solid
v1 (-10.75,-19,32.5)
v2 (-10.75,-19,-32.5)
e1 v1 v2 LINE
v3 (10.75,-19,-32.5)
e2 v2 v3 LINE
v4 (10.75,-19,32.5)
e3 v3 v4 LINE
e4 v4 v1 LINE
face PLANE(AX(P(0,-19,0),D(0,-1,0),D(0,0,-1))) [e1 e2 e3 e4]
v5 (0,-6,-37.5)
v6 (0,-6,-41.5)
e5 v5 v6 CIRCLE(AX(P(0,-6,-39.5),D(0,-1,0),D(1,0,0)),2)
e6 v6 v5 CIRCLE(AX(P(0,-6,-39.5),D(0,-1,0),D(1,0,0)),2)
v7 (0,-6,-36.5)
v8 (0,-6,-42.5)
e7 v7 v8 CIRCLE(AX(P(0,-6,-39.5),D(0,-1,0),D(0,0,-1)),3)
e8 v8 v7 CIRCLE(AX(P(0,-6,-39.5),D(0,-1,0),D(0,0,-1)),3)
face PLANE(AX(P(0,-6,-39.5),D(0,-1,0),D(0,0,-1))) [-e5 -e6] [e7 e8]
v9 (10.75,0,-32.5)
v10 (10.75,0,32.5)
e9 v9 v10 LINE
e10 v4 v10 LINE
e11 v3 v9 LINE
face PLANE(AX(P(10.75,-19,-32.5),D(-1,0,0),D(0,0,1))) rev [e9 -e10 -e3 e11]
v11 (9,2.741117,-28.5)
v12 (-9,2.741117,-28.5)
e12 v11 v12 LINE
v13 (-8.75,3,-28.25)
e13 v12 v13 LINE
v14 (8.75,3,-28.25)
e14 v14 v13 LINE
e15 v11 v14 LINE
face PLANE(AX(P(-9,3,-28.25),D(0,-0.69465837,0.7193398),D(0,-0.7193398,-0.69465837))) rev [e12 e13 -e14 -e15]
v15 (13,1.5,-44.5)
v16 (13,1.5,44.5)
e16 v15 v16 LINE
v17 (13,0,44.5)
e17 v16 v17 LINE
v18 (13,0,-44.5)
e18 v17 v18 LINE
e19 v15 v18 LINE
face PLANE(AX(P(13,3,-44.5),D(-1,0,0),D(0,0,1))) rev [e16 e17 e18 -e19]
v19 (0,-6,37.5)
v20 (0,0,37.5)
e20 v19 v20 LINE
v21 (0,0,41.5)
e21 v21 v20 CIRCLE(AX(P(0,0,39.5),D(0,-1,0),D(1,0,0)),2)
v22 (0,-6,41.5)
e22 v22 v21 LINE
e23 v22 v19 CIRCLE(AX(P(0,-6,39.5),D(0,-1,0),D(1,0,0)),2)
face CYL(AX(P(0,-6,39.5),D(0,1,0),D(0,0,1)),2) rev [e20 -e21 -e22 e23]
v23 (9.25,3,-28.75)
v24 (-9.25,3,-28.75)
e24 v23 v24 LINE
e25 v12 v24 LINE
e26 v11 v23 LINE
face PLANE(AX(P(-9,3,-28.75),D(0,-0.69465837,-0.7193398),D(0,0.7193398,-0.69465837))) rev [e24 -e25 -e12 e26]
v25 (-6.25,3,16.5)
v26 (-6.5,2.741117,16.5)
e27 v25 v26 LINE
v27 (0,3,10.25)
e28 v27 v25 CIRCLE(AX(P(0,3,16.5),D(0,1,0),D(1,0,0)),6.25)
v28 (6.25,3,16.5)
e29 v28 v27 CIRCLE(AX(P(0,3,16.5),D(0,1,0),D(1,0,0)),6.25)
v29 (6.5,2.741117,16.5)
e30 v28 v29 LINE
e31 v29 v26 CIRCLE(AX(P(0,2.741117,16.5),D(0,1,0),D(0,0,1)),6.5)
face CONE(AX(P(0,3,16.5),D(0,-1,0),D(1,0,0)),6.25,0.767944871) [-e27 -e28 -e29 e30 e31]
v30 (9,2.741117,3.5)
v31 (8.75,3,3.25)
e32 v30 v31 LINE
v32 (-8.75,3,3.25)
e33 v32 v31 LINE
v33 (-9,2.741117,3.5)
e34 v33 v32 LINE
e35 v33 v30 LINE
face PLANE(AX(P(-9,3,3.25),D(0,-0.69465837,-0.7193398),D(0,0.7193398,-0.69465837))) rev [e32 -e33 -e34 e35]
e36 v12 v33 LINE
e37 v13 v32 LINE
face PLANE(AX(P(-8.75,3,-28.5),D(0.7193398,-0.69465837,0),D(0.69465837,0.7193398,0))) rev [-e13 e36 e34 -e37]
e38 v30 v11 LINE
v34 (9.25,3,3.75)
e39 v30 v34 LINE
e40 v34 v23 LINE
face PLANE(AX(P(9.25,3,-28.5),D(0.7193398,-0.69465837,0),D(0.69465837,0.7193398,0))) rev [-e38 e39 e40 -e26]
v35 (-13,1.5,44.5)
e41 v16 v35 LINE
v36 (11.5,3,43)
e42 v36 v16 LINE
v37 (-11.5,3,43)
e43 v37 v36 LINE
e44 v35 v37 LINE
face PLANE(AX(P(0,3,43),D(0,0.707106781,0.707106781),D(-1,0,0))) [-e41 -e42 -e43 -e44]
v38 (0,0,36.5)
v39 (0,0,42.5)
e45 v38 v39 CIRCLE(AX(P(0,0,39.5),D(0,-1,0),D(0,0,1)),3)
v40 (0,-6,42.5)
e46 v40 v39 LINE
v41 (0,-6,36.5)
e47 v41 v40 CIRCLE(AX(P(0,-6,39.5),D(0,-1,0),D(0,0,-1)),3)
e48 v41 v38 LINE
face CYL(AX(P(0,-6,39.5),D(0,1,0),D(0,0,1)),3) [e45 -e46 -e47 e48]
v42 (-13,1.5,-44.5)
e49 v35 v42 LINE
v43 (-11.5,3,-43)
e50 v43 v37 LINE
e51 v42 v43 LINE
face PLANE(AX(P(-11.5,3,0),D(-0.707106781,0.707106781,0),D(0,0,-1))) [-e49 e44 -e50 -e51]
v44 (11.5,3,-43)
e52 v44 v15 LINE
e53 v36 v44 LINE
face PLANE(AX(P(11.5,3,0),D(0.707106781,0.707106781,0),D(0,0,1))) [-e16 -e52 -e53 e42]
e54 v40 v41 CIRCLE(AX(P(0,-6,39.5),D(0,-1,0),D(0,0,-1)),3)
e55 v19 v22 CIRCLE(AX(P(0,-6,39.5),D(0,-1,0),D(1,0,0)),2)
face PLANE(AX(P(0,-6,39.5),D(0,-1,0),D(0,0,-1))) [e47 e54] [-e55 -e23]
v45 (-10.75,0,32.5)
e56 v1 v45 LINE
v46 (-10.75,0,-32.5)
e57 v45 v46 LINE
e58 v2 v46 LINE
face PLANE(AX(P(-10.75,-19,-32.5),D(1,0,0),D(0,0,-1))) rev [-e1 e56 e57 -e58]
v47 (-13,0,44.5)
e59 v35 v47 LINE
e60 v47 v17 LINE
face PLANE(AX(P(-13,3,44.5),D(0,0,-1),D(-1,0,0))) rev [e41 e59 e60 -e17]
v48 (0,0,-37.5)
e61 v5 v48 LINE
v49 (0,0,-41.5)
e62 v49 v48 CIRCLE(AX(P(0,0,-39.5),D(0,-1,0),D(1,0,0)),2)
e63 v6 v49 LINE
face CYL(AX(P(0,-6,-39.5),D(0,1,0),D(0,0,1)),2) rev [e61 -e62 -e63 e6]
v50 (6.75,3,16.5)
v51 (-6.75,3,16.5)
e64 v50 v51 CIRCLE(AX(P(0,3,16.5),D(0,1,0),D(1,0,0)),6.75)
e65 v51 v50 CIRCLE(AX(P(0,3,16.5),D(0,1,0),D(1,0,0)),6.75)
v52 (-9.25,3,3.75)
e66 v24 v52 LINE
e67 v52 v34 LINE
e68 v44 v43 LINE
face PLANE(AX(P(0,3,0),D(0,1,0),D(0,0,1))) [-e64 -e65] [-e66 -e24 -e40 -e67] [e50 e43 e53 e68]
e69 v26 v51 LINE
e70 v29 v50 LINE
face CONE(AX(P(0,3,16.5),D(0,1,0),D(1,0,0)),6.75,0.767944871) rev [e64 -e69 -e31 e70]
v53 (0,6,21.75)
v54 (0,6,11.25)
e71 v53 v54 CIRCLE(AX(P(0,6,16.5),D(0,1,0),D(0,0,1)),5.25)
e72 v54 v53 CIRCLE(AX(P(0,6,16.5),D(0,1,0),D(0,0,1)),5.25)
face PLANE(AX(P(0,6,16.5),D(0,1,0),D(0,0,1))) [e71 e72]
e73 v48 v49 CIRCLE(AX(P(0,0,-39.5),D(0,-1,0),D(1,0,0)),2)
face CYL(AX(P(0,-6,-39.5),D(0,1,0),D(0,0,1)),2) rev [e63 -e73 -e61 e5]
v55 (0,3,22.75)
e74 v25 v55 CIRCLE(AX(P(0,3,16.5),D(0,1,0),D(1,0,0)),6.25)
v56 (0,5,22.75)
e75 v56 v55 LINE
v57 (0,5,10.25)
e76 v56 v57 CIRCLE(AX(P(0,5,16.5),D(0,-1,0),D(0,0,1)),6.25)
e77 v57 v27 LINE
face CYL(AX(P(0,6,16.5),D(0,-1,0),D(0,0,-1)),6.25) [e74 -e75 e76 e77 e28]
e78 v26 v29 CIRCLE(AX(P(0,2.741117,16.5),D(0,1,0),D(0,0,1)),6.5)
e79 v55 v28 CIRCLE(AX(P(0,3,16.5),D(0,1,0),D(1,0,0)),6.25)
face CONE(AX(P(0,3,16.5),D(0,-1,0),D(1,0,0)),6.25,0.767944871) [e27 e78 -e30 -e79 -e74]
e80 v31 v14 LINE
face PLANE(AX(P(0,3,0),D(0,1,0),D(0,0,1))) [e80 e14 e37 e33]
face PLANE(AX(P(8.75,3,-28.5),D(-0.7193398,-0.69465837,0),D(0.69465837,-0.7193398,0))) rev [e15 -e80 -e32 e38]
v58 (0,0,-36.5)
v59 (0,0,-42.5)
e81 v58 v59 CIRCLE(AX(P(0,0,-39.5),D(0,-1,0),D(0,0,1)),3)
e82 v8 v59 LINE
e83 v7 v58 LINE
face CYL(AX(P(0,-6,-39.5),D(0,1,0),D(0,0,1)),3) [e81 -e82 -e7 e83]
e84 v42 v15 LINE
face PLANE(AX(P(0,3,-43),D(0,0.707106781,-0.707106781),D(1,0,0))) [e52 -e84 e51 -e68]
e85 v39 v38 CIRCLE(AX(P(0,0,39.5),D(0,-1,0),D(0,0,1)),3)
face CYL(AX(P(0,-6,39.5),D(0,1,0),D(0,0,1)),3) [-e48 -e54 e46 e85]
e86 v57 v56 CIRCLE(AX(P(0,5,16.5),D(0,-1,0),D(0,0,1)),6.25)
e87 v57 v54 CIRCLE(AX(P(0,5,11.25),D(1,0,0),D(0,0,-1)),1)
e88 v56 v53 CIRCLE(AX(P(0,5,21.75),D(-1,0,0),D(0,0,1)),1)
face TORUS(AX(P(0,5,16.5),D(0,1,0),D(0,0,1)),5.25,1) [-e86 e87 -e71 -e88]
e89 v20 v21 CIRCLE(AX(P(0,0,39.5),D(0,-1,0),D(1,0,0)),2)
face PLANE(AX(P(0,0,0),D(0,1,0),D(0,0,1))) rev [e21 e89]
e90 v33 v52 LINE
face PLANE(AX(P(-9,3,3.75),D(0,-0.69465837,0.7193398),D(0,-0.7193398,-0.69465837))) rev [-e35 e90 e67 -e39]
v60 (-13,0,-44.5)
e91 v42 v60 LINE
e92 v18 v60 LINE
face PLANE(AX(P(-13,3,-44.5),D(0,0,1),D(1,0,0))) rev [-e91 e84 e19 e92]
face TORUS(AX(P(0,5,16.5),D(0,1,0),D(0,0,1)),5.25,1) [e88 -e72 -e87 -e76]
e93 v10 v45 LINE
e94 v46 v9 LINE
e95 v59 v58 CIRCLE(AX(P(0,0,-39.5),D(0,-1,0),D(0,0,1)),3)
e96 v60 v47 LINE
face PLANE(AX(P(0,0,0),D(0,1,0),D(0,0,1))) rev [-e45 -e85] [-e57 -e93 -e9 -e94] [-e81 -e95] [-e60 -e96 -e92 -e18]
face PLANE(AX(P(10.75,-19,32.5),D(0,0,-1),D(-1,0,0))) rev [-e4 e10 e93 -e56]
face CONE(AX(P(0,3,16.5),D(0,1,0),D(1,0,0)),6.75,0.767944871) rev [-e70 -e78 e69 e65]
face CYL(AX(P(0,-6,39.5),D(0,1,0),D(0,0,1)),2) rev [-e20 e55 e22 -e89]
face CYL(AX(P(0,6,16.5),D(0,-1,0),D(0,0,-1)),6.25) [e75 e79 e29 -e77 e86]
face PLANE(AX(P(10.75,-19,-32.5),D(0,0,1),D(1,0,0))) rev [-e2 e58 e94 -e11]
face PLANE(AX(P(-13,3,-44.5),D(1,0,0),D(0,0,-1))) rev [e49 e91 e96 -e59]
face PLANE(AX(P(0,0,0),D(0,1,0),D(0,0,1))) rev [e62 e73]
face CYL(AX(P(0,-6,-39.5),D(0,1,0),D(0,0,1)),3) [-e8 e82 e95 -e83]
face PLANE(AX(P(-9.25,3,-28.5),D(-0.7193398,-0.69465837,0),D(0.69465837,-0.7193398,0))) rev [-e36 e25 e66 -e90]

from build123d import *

# Parameters (mm, degrees)
SKETCH1_W               = 26
SKETCH1_H               = 89
BOSS_EXTRUDE1_DEPTH     = 3
SKETCH2_R               = 6.75
SKETCH2_R_2             = 6.25
SKETCH2_W               = 18.5
SKETCH2_H               = 32.5
SKETCH2_W_2             = 17.5
SKETCH2_H_2             = 31.5
CUT_EXTRUDE_THIN1_DEPTH = 1
CUT_EXTRUDE_THIN1_TAPER = 44
SKETCH3_R               = 6.25
BOSS_EXTRUDE2_DEPTH     = 3
FILLET1_R               = 1
CHAMFER1_SIZE           = 1.5
SKETCH4_R               = 3
SKETCH4_R_2             = 2
EXTRUDE_THIN2_DEPTH     = 6
SKETCH5_W               = 21.5
SKETCH5_H               = 65
BOSS_EXTRUDE3_DEPTH     = 19


with BuildPart() as part:
    # Sketch1 → Boss-Extrude1 (new body)
    with BuildSketch(Plane(origin=(0, 0, 0), x_dir=(1, 0, 0), z_dir=(0, 1, 0))):
        Rectangle(SKETCH1_W, SKETCH1_H)
    extrude(amount=BOSS_EXTRUDE1_DEPTH)

    # Sketch2 → Cut-Extrude-Thin1 (cut)
    # profile 1 of 2: a face of its own
    with BuildSketch(Plane(origin=(0, 3, 0), x_dir=(1, 0, 0), z_dir=(0, 1, 0))):
        with Locations((0, -16.5)):
            Circle(SKETCH2_R)
        with Locations((0, -16.5)):
            Circle(SKETCH2_R_2, mode=Mode.SUBTRACT)
    # profile 2 of 2: a face of its own
    with BuildSketch(Plane(origin=(0, 3, 0), x_dir=(1, 0, 0), z_dir=(0, 1, 0))):
        with Locations((0, 12.5)):
            Rectangle(SKETCH2_W, SKETCH2_H)
        with Locations((0, 12.5)):
            Rectangle(SKETCH2_W_2, SKETCH2_H_2, mode=Mode.SUBTRACT)
    extrude(amount=-CUT_EXTRUDE_THIN1_DEPTH, taper=CUT_EXTRUDE_THIN1_TAPER, mode=Mode.SUBTRACT)

    # Sketch3 → Boss-Extrude2 (add)
    with BuildSketch(Plane(origin=(0, 3, 0), x_dir=(1, 0, 0), z_dir=(0, 1, 0))):
        with Locations((0, -16.5)):
            Circle(SKETCH3_R)
    extrude(amount=BOSS_EXTRUDE2_DEPTH)

    # Fillet1
    fillet1_edges = [part.edges().sort_by_distance(p)[0] for p in [
        (-6.25, 6, 16.5),
    ]]
    fillet(fillet1_edges, radius=FILLET1_R)

    # Chamfer1
    chamfer1_edges = [part.edges().sort_by_distance(p)[0] for p in [
        (-13, 3, 0),
        (0, 3, 44.5),
        (13, 3, 0),
        (0, 3, -44.5),
    ]]
    chamfer(chamfer1_edges, length=CHAMFER1_SIZE)

    # Sketch4 → Extrude-Thin2 (add)
    # profile 1 of 2: a face of its own
    with BuildSketch(Plane.XZ):
        with Locations((0, -39.5)):
            Circle(SKETCH4_R)
        with Locations((0, -39.5)):
            Circle(SKETCH4_R_2, mode=Mode.SUBTRACT)
    # profile 2 of 2: a face of its own
    with BuildSketch(Plane.XZ):
        with Locations((0, 39.5)):
            Circle(SKETCH4_R)
        with Locations((0, 39.5)):
            Circle(SKETCH4_R_2, mode=Mode.SUBTRACT)
    extrude(amount=EXTRUDE_THIN2_DEPTH)

    # Sketch5 → Boss-Extrude3 (add)
    with BuildSketch(Plane.XZ):
        Rectangle(SKETCH5_W, SKETCH5_H)
    extrude(amount=BOSS_EXTRUDE3_DEPTH)


solid = part.part
